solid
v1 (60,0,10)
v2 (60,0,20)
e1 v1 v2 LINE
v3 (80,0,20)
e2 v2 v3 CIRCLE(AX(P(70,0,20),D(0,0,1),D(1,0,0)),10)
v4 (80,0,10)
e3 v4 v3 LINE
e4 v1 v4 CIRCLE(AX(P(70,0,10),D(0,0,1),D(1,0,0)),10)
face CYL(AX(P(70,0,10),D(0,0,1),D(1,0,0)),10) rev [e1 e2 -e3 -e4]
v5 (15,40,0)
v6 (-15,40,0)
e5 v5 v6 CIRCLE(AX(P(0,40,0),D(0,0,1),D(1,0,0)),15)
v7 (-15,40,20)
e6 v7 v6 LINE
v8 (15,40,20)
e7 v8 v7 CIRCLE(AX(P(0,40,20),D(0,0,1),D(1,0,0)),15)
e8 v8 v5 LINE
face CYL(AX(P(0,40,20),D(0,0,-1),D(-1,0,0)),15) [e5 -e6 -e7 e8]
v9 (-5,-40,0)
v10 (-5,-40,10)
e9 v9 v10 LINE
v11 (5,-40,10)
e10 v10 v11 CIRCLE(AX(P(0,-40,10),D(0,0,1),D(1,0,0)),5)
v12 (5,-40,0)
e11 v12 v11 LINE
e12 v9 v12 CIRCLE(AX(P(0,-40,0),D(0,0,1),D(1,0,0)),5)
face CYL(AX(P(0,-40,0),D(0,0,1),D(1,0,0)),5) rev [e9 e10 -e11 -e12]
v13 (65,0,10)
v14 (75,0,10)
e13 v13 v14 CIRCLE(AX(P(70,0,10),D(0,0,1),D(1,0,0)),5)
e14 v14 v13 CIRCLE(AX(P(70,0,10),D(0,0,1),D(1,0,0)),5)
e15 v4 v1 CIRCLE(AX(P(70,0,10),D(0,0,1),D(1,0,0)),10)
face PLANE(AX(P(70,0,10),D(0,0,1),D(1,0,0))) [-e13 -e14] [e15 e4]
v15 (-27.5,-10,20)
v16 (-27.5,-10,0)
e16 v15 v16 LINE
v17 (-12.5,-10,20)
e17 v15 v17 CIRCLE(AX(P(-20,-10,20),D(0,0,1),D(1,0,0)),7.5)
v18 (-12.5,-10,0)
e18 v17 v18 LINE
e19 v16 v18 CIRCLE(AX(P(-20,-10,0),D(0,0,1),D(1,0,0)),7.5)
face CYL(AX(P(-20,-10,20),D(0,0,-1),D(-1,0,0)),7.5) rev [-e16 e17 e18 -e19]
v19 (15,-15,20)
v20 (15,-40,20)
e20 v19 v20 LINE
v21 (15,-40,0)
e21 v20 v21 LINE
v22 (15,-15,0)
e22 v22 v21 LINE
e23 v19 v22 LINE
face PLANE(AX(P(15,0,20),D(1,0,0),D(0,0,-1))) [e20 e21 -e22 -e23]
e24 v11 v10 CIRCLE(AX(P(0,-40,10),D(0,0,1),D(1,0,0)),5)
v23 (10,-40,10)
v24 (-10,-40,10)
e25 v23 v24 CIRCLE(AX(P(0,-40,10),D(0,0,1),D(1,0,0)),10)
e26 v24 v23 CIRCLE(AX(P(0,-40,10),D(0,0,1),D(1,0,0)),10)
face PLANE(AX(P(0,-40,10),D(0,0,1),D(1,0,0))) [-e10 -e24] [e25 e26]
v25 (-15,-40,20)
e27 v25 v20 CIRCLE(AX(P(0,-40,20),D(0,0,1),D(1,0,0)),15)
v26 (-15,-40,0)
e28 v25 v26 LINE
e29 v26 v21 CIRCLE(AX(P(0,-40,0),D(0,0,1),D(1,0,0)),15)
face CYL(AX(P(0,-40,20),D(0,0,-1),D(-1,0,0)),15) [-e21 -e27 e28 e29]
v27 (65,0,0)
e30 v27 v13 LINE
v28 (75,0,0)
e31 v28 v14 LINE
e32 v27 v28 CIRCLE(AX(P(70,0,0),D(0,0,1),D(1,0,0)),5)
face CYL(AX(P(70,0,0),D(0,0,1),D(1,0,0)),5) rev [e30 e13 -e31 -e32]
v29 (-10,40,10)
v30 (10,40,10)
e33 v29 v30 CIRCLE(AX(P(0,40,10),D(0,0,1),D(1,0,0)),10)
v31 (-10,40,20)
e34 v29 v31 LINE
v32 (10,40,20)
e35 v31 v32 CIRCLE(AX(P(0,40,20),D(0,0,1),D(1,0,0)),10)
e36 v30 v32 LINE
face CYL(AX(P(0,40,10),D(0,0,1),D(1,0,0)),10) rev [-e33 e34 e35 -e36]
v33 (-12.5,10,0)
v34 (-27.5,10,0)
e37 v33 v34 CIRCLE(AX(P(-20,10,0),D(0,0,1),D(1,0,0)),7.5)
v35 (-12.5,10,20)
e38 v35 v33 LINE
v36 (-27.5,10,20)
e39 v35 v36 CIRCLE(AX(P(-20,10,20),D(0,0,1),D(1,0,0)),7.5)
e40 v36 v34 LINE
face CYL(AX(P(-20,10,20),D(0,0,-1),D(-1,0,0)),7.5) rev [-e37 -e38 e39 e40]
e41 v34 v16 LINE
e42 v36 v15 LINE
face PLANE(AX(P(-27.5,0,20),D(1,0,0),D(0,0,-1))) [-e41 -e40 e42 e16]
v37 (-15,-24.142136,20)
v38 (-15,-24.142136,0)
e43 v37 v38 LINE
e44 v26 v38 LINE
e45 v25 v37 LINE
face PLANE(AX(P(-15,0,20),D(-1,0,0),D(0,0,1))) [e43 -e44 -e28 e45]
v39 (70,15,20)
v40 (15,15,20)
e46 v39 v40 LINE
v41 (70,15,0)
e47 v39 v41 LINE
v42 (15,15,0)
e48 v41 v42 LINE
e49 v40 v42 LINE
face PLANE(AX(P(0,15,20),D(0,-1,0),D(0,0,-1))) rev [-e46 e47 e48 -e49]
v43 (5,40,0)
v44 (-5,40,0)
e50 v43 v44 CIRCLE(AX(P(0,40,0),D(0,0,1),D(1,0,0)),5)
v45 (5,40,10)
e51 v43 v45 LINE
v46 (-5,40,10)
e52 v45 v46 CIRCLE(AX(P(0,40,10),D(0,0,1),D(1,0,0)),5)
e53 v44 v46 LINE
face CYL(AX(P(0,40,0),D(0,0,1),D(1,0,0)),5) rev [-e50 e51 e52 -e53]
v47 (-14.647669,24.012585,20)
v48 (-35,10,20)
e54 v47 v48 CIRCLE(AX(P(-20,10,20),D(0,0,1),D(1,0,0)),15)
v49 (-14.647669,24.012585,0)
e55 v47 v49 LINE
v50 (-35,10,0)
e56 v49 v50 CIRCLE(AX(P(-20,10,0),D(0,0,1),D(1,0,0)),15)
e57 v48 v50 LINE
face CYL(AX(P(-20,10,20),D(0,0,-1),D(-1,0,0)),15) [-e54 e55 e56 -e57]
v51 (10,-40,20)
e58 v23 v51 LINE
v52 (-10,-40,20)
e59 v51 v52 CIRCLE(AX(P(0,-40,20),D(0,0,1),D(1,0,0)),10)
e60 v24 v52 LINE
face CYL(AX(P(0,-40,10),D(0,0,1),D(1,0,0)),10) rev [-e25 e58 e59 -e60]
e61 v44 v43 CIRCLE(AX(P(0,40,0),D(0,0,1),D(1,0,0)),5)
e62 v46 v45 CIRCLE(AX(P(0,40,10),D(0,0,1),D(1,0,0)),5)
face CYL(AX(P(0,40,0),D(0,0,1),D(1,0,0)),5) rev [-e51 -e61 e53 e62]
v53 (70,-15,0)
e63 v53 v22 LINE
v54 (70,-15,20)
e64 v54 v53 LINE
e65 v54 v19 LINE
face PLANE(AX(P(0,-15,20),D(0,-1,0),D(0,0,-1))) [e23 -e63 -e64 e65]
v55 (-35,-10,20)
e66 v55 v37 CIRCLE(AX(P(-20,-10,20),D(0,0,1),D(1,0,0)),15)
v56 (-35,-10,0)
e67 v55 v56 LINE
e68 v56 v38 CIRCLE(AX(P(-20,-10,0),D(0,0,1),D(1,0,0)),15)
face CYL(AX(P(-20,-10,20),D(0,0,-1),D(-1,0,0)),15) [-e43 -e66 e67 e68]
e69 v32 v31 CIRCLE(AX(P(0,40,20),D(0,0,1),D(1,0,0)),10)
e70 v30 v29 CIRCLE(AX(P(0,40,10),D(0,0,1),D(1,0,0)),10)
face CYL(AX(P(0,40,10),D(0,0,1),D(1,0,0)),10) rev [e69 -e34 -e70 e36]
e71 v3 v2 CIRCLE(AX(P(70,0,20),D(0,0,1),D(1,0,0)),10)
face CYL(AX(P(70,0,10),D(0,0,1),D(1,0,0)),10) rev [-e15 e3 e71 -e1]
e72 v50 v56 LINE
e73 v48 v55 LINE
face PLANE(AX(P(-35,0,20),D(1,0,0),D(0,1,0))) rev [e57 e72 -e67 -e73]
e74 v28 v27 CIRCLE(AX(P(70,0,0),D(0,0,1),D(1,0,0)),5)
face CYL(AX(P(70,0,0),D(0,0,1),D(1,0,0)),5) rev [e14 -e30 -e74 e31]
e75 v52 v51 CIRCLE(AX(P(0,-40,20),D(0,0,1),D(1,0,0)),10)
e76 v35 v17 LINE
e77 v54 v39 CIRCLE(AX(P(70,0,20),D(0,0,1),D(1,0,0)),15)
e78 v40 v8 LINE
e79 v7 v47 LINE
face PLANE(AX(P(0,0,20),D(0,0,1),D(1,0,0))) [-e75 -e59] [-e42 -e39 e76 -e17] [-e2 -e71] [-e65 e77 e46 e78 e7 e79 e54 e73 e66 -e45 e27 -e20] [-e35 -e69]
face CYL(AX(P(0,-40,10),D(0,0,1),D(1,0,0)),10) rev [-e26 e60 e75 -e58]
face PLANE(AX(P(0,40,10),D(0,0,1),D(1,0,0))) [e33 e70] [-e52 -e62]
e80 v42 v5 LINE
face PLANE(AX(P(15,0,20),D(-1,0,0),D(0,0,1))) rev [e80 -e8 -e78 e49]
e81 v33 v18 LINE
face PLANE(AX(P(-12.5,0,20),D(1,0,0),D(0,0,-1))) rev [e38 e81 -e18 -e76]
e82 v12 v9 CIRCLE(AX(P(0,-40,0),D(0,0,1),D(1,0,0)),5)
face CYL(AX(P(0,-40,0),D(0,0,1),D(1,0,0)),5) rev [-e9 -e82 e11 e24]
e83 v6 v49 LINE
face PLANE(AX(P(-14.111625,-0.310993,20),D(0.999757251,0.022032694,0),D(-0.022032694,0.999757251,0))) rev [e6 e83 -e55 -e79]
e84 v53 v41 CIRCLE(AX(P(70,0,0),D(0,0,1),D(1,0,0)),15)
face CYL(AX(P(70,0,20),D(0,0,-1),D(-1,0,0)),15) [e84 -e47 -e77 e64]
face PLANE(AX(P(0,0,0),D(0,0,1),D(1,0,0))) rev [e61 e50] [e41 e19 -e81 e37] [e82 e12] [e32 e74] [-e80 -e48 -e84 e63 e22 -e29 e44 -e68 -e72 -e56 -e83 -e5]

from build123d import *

# Parameters (mm, degrees)
T_BRACKET_PLATE_20MM_DEPTH     = 20
POCKET_A_SKETCH_R              = 10
TRIANGULAR_POCKET_A_10MM_DEPTH = 10
POCKET_B_SKETCH_R              = 5
TRIANGULAR_POCKET_B_10MM_DEPTH = 10


with BuildPart() as part:
    # T Profile Sketch → T Bracket Plate 20mm (new body)
    with BuildSketch(Plane.XY):
        with BuildLine():
            ThreePointArc((-14.647668653, 24.012585384), (-28.506322055, 22.354856741), (-35, 10))
            Line((-35, 10), (-35, -10))
            ThreePointArc((-35, -10), (-28.660254038, -22.247448714), (-15, -24.142135624))
            Line((-15, -24.142135624), (-15, -40))
            ThreePointArc((-15, -40), (0, -55), (15, -40))
            Line((15, -40), (15, -15))
            Line((15, -15), (70, -15))
            ThreePointArc((70, -15), (85, 0), (70, 15))
            Line((70, 15), (15, 15))
            Line((15, 15), (15, 40))
            ThreePointArc((15, 40), (0, 55), (-15, 40))
            Line((-15, 40), (-14.985436811, 39.339179624))
            Line((-14.985436811, 39.339179624), (-14.647668653, 24.012585384))
        make_face()
        with BuildLine():
            Line((-27.5, -10), (-27.5, 10))
            ThreePointArc((-27.5, 10), (-20, 17.5), (-12.5, 10))
            Line((-12.5, 10), (-12.5, -10))
            ThreePointArc((-12.5, -10), (-20, -17.5), (-27.5, -10))
        make_face(mode=Mode.SUBTRACT)
    extrude(amount=T_BRACKET_PLATE_20MM_DEPTH)

    # Pocket A Sketch → Triangular Pocket A 10mm (cut)
    with BuildSketch(Plane.XY.offset(20)):
        with Locations((0, 40)):
            Circle(POCKET_A_SKETCH_R)
        with Locations((0, -40)):
            Circle(POCKET_A_SKETCH_R)
        with Locations((70, 0)):
            Circle(POCKET_A_SKETCH_R)
    extrude(amount=-TRIANGULAR_POCKET_A_10MM_DEPTH, mode=Mode.SUBTRACT)

    # Pocket B Sketch → Triangular Pocket B 10mm (cut)
    with BuildSketch(Plane.XY.offset(10)):
        with Locations((0, 40)):
            Circle(POCKET_B_SKETCH_R)
        with Locations((0, -40)):
            Circle(POCKET_B_SKETCH_R)
        with Locations((70, 0)):
            Circle(POCKET_B_SKETCH_R)
    extrude(amount=-TRIANGULAR_POCKET_B_10MM_DEPTH, mode=Mode.SUBTRACT)


solid = part.part
